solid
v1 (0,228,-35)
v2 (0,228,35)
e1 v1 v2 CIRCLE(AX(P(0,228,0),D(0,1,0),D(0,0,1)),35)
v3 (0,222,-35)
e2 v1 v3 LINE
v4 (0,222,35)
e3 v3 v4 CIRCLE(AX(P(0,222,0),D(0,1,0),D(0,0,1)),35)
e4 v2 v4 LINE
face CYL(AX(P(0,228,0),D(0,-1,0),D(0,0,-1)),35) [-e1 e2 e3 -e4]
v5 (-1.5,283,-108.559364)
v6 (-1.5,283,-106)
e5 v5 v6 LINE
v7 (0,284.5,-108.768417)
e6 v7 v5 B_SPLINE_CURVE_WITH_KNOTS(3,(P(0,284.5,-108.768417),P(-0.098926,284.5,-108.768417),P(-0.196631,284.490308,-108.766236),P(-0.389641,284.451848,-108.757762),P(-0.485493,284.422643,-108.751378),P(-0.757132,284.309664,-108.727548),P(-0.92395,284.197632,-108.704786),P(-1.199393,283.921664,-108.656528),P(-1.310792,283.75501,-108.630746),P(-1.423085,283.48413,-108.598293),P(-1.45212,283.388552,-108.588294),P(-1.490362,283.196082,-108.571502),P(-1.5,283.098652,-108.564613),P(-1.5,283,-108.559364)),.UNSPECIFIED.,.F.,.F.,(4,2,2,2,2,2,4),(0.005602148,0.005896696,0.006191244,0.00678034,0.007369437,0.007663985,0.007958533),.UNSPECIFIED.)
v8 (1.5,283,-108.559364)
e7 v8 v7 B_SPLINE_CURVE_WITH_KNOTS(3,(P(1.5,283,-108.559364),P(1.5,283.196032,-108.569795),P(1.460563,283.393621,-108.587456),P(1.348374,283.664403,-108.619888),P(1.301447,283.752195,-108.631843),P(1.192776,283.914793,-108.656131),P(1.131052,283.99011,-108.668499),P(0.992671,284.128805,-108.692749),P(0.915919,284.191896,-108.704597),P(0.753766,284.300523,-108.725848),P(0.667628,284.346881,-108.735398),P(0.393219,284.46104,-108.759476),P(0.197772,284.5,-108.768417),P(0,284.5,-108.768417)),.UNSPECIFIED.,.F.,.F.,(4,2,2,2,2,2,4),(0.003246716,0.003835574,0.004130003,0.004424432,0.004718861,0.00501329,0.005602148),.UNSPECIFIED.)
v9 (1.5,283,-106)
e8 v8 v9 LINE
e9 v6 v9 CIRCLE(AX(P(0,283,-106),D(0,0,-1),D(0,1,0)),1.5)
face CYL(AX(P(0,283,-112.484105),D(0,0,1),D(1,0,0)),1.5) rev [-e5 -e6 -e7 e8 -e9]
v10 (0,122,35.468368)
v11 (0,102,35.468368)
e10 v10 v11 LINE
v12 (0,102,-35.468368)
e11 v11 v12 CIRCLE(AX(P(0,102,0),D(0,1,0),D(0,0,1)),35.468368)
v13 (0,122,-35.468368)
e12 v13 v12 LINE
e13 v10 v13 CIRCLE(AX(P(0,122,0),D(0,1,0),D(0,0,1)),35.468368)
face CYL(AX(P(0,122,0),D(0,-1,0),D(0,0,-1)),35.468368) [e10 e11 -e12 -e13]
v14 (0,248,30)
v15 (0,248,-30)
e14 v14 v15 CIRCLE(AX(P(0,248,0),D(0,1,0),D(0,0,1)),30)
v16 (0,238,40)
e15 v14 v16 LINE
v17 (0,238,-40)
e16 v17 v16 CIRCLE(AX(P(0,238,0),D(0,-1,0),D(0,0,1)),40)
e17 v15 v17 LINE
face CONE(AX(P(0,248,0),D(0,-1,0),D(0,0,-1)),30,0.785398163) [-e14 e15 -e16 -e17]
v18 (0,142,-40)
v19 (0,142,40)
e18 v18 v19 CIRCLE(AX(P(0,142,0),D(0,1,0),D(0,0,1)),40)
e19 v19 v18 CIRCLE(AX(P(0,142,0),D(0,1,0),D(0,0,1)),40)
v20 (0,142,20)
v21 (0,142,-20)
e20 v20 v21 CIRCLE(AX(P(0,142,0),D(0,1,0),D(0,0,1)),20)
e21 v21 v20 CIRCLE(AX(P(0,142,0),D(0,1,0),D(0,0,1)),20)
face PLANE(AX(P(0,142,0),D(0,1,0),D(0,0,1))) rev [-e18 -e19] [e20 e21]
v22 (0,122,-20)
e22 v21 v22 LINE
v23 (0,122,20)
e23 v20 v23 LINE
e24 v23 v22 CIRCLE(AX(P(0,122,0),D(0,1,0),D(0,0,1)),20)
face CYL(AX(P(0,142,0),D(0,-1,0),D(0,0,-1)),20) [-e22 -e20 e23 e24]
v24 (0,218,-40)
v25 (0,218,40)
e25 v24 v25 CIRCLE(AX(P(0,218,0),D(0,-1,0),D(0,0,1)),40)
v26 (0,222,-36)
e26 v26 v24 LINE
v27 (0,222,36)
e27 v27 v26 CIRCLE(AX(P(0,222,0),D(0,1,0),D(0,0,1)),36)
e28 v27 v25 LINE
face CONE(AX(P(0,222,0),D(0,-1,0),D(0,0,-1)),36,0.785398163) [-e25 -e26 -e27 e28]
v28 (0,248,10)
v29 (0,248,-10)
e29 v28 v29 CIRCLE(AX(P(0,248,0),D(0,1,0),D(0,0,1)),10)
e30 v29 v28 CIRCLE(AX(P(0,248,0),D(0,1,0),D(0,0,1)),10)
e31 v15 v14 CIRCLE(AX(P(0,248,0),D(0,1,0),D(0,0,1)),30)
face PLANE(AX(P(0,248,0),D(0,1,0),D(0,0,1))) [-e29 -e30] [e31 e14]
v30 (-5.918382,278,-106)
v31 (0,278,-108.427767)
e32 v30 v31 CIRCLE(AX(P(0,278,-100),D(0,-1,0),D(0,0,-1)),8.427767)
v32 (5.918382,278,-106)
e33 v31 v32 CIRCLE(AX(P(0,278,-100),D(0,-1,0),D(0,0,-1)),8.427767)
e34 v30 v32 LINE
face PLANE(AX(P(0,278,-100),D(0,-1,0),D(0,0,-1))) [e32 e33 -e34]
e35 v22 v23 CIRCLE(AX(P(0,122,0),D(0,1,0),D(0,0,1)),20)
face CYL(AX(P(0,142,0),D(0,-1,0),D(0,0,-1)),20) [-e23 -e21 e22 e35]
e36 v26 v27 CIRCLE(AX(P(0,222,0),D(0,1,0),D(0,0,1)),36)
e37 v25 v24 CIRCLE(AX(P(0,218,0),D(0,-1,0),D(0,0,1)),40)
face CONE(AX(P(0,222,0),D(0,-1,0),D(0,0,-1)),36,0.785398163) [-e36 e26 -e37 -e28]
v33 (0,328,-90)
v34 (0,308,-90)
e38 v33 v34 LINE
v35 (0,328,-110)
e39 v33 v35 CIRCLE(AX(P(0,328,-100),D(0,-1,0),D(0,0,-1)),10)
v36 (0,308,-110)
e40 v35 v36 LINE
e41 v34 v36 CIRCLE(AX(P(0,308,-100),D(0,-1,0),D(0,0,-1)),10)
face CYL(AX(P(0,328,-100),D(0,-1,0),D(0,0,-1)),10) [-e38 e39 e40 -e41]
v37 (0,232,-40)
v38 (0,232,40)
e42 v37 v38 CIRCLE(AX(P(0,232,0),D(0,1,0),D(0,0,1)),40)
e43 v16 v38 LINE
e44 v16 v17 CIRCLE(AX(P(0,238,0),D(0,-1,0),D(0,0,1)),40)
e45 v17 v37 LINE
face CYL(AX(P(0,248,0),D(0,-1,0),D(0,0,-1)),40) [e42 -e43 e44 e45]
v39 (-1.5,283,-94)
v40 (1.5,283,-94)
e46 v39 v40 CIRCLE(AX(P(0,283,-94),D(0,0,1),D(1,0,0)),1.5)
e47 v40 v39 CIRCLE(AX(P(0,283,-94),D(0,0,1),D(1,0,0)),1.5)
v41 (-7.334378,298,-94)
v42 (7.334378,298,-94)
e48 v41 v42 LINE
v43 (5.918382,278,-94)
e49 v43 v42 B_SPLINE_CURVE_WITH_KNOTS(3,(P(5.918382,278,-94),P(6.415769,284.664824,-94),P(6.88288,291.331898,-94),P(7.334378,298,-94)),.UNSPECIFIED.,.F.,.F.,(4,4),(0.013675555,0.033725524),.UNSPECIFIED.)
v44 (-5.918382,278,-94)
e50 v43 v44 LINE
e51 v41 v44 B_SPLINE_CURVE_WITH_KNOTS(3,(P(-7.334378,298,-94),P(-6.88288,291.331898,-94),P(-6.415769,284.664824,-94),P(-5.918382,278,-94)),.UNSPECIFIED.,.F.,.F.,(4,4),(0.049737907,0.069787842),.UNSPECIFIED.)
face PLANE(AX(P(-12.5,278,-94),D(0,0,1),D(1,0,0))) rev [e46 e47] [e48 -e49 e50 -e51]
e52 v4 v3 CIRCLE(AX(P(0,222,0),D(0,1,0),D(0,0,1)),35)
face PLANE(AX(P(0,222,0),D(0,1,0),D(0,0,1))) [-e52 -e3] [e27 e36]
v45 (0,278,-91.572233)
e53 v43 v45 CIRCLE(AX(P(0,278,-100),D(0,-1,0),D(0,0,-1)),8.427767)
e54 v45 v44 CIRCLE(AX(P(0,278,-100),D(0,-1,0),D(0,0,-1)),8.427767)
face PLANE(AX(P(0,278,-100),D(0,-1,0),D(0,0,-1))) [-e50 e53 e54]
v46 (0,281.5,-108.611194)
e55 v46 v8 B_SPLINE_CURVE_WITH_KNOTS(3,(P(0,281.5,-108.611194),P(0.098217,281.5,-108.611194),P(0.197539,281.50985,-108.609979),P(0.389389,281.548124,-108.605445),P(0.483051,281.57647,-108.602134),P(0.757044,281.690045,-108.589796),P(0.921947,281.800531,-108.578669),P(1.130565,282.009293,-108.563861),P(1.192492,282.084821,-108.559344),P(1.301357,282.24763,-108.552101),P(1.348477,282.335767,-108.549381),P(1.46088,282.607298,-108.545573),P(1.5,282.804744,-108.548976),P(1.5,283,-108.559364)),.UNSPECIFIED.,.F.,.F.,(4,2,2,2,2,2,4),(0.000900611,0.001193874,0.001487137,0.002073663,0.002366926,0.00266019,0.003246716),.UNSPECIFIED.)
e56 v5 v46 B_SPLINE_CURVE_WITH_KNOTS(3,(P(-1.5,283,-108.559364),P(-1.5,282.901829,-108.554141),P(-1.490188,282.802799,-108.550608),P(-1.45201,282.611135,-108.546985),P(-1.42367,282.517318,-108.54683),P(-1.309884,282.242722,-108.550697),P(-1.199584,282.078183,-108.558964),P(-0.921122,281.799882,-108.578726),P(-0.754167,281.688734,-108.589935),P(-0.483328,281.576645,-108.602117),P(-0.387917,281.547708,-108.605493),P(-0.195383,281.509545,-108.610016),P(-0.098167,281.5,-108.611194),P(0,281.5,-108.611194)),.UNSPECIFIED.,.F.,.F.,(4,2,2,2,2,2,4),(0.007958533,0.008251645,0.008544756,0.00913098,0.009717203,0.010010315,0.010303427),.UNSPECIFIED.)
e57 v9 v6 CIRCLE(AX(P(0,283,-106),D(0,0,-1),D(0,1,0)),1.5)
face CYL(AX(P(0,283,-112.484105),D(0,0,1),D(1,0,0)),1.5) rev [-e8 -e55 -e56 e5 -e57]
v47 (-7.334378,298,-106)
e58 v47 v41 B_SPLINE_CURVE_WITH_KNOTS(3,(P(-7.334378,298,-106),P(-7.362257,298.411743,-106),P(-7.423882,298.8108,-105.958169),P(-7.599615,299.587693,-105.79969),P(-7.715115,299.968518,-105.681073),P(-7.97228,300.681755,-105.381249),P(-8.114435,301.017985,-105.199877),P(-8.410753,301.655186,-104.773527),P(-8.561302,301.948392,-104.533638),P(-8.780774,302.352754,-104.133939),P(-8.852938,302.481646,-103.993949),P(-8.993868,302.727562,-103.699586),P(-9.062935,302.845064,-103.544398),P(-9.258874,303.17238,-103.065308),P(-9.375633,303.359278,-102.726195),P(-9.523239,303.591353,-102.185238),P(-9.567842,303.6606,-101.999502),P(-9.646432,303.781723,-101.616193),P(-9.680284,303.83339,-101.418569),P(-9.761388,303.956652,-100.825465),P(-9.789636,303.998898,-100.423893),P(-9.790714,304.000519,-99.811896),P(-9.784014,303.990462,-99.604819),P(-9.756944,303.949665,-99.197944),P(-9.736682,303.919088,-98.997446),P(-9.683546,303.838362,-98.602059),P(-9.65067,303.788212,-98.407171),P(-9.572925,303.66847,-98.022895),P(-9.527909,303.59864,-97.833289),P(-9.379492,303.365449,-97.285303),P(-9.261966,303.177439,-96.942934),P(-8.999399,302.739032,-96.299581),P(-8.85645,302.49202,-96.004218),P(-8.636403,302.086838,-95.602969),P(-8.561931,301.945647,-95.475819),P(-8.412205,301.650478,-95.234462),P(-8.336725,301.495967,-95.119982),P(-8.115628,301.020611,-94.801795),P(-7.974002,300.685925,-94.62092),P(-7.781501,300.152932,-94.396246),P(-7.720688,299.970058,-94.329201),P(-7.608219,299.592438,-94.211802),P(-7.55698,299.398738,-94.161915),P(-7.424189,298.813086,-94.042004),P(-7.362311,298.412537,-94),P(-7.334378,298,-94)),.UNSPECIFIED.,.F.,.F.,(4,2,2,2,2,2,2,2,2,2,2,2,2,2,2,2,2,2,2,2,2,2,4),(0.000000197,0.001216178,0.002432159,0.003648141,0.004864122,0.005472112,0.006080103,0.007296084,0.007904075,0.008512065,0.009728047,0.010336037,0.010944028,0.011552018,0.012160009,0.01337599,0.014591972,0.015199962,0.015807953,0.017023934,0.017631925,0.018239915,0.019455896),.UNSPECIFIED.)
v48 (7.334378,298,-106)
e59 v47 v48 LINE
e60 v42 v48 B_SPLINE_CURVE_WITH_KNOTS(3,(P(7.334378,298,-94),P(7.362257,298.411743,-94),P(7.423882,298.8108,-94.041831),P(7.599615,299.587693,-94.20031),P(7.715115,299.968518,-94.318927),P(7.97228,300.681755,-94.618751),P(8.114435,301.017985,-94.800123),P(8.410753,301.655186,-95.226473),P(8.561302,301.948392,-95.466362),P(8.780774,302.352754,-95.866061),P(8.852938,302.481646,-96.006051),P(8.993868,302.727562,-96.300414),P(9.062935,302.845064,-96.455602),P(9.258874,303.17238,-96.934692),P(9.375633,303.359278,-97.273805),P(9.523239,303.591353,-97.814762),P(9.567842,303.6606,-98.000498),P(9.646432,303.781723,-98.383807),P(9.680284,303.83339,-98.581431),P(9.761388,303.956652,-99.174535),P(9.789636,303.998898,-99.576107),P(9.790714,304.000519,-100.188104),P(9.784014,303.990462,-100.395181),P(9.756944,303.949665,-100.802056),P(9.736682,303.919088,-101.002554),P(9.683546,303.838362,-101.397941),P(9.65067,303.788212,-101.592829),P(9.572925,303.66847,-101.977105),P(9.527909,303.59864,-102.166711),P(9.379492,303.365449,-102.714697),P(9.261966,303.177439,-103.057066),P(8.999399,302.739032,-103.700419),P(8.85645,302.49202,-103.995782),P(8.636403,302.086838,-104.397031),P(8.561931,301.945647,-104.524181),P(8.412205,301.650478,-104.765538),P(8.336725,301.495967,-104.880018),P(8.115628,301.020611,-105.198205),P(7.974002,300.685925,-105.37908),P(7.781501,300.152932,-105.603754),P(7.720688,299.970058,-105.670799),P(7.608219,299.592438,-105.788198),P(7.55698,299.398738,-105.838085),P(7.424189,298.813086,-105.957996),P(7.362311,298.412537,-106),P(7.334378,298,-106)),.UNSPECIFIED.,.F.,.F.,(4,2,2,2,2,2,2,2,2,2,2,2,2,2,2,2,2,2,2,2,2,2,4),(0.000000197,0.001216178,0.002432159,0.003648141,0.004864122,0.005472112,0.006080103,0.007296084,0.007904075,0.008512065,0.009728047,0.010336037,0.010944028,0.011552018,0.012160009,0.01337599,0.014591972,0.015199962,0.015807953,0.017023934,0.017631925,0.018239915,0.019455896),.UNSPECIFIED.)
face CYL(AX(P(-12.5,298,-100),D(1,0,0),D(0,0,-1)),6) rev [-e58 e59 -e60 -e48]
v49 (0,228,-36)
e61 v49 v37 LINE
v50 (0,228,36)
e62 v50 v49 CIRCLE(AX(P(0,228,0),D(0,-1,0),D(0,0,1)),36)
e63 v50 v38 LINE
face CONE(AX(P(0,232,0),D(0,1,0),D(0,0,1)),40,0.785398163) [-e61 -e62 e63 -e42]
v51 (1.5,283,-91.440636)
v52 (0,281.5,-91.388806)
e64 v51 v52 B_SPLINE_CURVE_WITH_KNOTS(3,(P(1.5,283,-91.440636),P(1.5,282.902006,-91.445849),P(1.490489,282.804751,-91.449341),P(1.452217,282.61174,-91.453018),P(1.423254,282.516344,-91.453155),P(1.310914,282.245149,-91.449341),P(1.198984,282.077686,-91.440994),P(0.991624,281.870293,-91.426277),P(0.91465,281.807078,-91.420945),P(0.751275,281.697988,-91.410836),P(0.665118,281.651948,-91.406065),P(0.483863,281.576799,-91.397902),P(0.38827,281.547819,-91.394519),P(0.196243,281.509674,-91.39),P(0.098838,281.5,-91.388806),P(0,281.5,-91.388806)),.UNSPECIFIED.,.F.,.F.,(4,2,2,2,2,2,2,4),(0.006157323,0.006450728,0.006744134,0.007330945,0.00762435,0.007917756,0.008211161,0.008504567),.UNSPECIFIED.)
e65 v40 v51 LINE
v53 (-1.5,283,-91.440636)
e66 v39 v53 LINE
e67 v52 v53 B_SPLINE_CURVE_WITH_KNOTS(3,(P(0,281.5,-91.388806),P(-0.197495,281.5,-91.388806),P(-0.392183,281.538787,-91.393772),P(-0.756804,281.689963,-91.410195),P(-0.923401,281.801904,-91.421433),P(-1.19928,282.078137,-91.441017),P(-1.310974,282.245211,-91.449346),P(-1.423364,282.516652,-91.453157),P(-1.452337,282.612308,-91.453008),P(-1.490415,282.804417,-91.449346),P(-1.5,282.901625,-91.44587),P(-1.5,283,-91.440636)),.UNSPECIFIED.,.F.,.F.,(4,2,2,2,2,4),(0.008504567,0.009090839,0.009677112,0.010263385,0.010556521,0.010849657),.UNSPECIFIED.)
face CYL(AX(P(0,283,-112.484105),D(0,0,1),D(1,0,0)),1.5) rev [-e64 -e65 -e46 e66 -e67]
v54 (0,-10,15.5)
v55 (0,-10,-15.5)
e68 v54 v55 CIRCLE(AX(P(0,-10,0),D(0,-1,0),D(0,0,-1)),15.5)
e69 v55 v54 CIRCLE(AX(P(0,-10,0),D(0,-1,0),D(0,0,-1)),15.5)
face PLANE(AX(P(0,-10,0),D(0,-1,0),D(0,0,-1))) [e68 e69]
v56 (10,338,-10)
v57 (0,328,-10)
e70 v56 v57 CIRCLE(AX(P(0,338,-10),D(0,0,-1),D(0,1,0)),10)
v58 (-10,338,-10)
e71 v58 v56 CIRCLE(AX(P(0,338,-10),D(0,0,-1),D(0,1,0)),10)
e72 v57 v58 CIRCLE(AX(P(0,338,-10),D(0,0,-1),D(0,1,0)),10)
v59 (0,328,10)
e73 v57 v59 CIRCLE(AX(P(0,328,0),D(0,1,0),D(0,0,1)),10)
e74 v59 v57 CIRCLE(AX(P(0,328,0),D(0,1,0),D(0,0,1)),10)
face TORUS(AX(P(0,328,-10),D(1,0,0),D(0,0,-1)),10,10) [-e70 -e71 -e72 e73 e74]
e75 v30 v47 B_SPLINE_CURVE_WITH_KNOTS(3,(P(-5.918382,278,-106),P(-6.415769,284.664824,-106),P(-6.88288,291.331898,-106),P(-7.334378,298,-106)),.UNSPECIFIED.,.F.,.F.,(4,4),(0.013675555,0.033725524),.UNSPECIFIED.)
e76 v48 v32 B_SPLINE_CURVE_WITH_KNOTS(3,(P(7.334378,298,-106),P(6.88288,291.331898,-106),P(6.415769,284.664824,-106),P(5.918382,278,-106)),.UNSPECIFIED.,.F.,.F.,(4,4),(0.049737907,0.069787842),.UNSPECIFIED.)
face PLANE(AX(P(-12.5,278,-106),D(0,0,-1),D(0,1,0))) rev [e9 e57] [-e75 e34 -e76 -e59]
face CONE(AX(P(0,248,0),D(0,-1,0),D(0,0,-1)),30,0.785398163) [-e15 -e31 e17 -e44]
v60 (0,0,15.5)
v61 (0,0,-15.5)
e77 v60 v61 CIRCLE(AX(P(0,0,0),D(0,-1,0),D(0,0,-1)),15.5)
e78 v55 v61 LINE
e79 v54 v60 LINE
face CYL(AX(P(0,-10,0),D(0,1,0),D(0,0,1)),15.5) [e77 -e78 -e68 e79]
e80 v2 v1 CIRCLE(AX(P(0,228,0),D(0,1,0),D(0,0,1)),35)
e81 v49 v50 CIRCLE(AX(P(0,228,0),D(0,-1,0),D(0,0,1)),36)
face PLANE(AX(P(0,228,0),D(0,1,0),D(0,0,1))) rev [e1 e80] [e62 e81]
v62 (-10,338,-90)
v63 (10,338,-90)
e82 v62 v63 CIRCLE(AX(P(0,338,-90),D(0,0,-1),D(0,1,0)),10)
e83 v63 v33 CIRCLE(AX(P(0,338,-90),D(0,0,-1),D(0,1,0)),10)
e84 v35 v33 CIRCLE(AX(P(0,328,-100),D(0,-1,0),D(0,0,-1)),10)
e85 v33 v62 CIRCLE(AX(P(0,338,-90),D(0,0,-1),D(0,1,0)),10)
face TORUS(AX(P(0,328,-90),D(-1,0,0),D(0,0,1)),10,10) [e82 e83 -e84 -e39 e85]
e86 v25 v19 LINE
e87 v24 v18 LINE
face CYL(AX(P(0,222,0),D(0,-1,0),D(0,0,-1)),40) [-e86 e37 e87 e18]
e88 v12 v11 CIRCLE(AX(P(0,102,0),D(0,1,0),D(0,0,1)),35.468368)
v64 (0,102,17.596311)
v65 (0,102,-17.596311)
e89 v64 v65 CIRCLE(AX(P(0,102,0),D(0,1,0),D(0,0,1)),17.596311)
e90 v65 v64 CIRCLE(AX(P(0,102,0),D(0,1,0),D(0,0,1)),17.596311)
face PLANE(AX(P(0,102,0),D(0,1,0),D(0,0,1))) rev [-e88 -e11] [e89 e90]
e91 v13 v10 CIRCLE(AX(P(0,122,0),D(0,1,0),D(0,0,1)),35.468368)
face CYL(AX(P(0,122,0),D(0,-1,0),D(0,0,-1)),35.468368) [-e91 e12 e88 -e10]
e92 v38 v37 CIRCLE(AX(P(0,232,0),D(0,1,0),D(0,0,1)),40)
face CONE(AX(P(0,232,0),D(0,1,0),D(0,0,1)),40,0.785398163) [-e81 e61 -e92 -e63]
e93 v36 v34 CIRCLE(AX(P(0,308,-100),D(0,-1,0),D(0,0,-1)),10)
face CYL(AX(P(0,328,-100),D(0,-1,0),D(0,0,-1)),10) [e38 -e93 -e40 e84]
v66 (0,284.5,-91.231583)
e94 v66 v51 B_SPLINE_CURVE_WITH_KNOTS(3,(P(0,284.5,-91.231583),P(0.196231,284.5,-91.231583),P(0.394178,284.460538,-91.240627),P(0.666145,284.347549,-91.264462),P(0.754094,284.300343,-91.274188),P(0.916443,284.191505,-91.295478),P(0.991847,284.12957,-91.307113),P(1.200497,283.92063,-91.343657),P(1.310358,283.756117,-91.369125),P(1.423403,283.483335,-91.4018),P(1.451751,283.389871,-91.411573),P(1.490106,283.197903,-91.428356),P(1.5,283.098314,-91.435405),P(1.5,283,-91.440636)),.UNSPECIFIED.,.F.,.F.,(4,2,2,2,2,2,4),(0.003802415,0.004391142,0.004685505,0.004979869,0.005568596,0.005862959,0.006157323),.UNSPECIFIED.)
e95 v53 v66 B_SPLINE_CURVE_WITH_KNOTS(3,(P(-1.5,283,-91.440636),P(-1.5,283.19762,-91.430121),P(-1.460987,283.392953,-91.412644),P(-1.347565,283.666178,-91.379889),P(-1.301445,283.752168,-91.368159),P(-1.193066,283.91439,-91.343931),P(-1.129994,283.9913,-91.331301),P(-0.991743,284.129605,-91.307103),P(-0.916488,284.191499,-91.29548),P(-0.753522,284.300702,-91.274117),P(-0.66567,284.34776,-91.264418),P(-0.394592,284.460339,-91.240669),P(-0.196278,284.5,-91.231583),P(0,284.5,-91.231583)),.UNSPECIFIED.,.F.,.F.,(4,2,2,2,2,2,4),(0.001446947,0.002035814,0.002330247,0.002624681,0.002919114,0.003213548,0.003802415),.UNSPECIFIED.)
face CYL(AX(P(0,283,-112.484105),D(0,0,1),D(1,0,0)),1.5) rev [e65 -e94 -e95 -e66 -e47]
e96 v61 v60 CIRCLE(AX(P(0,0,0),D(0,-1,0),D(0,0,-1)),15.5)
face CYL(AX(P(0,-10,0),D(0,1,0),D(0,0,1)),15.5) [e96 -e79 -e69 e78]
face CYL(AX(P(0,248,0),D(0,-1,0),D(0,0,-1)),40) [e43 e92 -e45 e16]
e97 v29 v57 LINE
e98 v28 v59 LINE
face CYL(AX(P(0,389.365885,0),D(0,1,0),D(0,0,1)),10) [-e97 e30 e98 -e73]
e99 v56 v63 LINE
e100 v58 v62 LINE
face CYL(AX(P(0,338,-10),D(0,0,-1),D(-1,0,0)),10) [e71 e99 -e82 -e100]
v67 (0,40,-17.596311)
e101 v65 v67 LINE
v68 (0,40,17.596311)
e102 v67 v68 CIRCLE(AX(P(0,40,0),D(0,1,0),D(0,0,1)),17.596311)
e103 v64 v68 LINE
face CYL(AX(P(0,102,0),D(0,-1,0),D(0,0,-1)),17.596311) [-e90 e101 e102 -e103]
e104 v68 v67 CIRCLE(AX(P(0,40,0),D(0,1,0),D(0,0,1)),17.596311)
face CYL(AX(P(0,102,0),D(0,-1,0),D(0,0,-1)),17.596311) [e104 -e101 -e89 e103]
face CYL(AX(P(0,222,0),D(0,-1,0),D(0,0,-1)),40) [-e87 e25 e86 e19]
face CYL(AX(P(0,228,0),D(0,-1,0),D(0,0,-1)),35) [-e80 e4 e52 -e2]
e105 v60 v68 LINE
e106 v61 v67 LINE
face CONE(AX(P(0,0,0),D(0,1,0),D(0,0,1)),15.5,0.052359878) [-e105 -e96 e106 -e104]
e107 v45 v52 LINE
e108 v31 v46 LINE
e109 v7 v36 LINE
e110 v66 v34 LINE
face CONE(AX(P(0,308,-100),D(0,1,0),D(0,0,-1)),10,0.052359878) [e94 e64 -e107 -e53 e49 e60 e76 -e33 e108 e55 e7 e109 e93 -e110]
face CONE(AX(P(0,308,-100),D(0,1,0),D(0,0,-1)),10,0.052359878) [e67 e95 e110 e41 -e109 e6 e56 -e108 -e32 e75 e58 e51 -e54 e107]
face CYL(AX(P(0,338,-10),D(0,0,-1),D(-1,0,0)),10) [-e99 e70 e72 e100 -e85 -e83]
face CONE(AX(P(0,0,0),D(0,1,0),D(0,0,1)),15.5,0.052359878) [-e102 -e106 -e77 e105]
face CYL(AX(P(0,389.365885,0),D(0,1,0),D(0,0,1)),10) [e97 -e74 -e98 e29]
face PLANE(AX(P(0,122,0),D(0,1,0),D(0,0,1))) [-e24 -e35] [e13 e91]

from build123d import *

# Parameters (mm, degrees)
SKETCH1_R           = 15.5
BOSS_EXTRUDE1_DEPTH = 40
BOSS_EXTRUDE1_DRAFT = -3
SKETCH2_R           = 15.5
BOSS_EXTRUDE2_DEPTH = 10
SKETCH3_R           = 17.596311171
BOSS_EXTRUDE3_DEPTH = 62
SKETCH4_R           = 35.468367634
BOSS_EXTRUDE4_DEPTH = 20
SKETCH5_R           = 20
BOSS_EXTRUDE5_DEPTH = 20
SKETCH6_R           = 40
BOSS_EXTRUDE6_DEPTH = 80
SKETCH7_R           = 35
BOSS_EXTRUDE7_DEPTH = 6
SKETCH8_R           = 40
BOSS_EXTRUDE8_DEPTH = 20
CHAMFER1_SIZE       = 10
CHAMFER2_SIZE       = 4
CHAMFER4_SIZE       = 4
SKETCH12_W          = 10
SKETCH12_H          = 80
SKETCH15_R          = 10
SKETCH17_R          = 10
BOSS_EXTRUDE9_DEPTH = 30
BOSS_EXTRUDE9_TAPER = 3
CUT_EXTRUDE1_DEPTH  = 12.5
SKETCH20_R          = 1.5
CUT_EXTRUDE2_DEPTH  = 12.5


with BuildPart() as part:
    # Sketch1 → Boss-Extrude1 (with draft: the straight prism first)
    with BuildSketch(Plane(origin=(0, 0, 0), x_dir=(1, 0, 0), z_dir=(0, 1, 0))):
        Circle(SKETCH1_R)
    extrude(amount=BOSS_EXTRUDE1_DEPTH)
    # Boss-Extrude1: the draft: its side faces are tilted about the plane it starts from
    boss_extrude1_sides = [part.faces().sort_by_distance(p)[0] for p in [
        (-15.5, 20, 0),
    ]]
    draft(boss_extrude1_sides, Plane(origin=(0, 0, 0), x_dir=(1, 0, 0), z_dir=(0, 1, 0)), BOSS_EXTRUDE1_DRAFT)

    # Sketch2 → Boss-Extrude2 (add)
    with BuildSketch(Plane.XZ):
        with Locations(Location((0, 0, 0), (0, 0, 270))):
            Circle(SKETCH2_R)
    extrude(amount=BOSS_EXTRUDE2_DEPTH)

    # Sketch3 → Boss-Extrude3 (add)
    with BuildSketch(Plane(origin=(0, 40, 0), x_dir=(1, 0, 0), z_dir=(0, 1, 0))):
        with Locations(Location((0, 0, 0), (0, 0, 270))):
            Circle(SKETCH3_R)
    extrude(amount=BOSS_EXTRUDE3_DEPTH)

    # Sketch4 → Boss-Extrude4 (add)
    with BuildSketch(Plane(origin=(0, 102, 0), x_dir=(1, 0, 0), z_dir=(0, 1, 0))):
        with Locations(Location((0, 0, 0), (0, 0, 270))):
            Circle(SKETCH4_R)
    extrude(amount=BOSS_EXTRUDE4_DEPTH)

    # Sketch5 → Boss-Extrude5 (add)
    with BuildSketch(Plane(origin=(0, 122, 0), x_dir=(1, 0, 0), z_dir=(0, 1, 0))):
        with Locations(Location((0, 0, 0), (0, 0, 270))):
            Circle(SKETCH5_R)
    extrude(amount=BOSS_EXTRUDE5_DEPTH)

    # Sketch6 → Boss-Extrude6 (add)
    with BuildSketch(Plane(origin=(0, 142, 0), x_dir=(1, 0, 0), z_dir=(0, 1, 0))):
        with Locations(Location((0, 0, 0), (0, 0, 270))):
            Circle(SKETCH6_R)
    extrude(amount=BOSS_EXTRUDE6_DEPTH)

    # Sketch7 → Boss-Extrude7 (add)
    with BuildSketch(Plane(origin=(0, 222, 0), x_dir=(1, 0, 0), z_dir=(0, 1, 0))):
        with Locations(Location((0, 0, 0), (0, 0, 270))):
            Circle(SKETCH7_R)
    extrude(amount=BOSS_EXTRUDE7_DEPTH)

    # Sketch8 → Boss-Extrude8 (add)
    with BuildSketch(Plane(origin=(0, 228, 0), x_dir=(1, 0, 0), z_dir=(0, 1, 0))):
        with Locations(Location((0, 0, 0), (0, 0, 270))):
            Circle(SKETCH8_R)
    extrude(amount=BOSS_EXTRUDE8_DEPTH)

    # Chamfer1
    chamfer1_edges = [part.edges().sort_by_distance(p)[0] for p in [
        (0, 248, -40),
    ]]
    chamfer(chamfer1_edges, length=CHAMFER1_SIZE)

    # Chamfer2
    chamfer2_edges = [part.edges().sort_by_distance(p)[0] for p in [
        (0, 222, -40),
    ]]
    chamfer(chamfer2_edges, length=CHAMFER2_SIZE)

    # Chamfer4
    chamfer4_edges = [part.edges().sort_by_distance(p)[0] for p in [
        (0, 228, -40),
    ]]
    chamfer(chamfer4_edges, length=CHAMFER4_SIZE)

    # Sketch12 → Revolve1 (revolve)
    with BuildSketch(Plane(origin=(0, 0, 0), x_dir=(0, 0, -1), z_dir=(1, 0, 0))):
        with Locations((-5, 288)):
            Rectangle(SKETCH12_W, SKETCH12_H)
    revolve(axis=Axis((0, 389.365885341, 0), (0, -1, 0)))

    # Sweep1: sweep along a path in Sketch14
    with BuildLine(Plane(origin=(0, 0, 0), x_dir=(0, 0, -1), z_dir=(1, 0, 0))) as sweep1_path:
        Line((100, 308), (100, 328))
        ThreePointArc((100, 328), (97.071067812, 335.071067812), (90, 338))
        Line((90, 338), (10, 338))
        ThreePointArc((10, 338), (2.928932188, 335.071067812), (0, 328))
    # Sketch15 → Sweep1 (sweep)
    with BuildSketch(Plane(origin=(0, 328, 0), x_dir=(1, 0, 0), z_dir=(0, 1, 0))):
        Circle(SKETCH15_R)
    sweep(path=sweep1_path.line)

    # Sketch17 → Boss-Extrude9 (add)
    with BuildSketch(Plane.XZ.offset(-308)):
        with Locations(Location((0, -100, 0), (0, 0, 270))):
            Circle(SKETCH17_R)
    extrude(amount=BOSS_EXTRUDE9_DEPTH, taper=BOSS_EXTRUDE9_TAPER)

    # Sketch19 → Cut-Extrude1 (cut, symmetric)
    with BuildSketch(Plane(origin=(0, 0, 0), x_dir=(0, 0, -1), z_dir=(1, 0, 0))):
        with BuildLine():
            Line((94, 278), (94, 298))
            ThreePointArc((94, 298), (100, 304), (106, 298))
            Line((106, 298), (106, 278))
            Line((106, 278), (94, 278))
        make_face()
    extrude(amount=CUT_EXTRUDE1_DEPTH, both=True, mode=Mode.SUBTRACT)

    # Sketch20 → Cut-Extrude2 (cut, symmetric)
    with BuildSketch(Plane.XY.offset(-99.984104739)):
        with Locations(Location((0, 283, 0), (0, 0, 90))):
            Circle(SKETCH20_R)
    extrude(amount=CUT_EXTRUDE2_DEPTH, both=True, mode=Mode.SUBTRACT)


solid = part.part
